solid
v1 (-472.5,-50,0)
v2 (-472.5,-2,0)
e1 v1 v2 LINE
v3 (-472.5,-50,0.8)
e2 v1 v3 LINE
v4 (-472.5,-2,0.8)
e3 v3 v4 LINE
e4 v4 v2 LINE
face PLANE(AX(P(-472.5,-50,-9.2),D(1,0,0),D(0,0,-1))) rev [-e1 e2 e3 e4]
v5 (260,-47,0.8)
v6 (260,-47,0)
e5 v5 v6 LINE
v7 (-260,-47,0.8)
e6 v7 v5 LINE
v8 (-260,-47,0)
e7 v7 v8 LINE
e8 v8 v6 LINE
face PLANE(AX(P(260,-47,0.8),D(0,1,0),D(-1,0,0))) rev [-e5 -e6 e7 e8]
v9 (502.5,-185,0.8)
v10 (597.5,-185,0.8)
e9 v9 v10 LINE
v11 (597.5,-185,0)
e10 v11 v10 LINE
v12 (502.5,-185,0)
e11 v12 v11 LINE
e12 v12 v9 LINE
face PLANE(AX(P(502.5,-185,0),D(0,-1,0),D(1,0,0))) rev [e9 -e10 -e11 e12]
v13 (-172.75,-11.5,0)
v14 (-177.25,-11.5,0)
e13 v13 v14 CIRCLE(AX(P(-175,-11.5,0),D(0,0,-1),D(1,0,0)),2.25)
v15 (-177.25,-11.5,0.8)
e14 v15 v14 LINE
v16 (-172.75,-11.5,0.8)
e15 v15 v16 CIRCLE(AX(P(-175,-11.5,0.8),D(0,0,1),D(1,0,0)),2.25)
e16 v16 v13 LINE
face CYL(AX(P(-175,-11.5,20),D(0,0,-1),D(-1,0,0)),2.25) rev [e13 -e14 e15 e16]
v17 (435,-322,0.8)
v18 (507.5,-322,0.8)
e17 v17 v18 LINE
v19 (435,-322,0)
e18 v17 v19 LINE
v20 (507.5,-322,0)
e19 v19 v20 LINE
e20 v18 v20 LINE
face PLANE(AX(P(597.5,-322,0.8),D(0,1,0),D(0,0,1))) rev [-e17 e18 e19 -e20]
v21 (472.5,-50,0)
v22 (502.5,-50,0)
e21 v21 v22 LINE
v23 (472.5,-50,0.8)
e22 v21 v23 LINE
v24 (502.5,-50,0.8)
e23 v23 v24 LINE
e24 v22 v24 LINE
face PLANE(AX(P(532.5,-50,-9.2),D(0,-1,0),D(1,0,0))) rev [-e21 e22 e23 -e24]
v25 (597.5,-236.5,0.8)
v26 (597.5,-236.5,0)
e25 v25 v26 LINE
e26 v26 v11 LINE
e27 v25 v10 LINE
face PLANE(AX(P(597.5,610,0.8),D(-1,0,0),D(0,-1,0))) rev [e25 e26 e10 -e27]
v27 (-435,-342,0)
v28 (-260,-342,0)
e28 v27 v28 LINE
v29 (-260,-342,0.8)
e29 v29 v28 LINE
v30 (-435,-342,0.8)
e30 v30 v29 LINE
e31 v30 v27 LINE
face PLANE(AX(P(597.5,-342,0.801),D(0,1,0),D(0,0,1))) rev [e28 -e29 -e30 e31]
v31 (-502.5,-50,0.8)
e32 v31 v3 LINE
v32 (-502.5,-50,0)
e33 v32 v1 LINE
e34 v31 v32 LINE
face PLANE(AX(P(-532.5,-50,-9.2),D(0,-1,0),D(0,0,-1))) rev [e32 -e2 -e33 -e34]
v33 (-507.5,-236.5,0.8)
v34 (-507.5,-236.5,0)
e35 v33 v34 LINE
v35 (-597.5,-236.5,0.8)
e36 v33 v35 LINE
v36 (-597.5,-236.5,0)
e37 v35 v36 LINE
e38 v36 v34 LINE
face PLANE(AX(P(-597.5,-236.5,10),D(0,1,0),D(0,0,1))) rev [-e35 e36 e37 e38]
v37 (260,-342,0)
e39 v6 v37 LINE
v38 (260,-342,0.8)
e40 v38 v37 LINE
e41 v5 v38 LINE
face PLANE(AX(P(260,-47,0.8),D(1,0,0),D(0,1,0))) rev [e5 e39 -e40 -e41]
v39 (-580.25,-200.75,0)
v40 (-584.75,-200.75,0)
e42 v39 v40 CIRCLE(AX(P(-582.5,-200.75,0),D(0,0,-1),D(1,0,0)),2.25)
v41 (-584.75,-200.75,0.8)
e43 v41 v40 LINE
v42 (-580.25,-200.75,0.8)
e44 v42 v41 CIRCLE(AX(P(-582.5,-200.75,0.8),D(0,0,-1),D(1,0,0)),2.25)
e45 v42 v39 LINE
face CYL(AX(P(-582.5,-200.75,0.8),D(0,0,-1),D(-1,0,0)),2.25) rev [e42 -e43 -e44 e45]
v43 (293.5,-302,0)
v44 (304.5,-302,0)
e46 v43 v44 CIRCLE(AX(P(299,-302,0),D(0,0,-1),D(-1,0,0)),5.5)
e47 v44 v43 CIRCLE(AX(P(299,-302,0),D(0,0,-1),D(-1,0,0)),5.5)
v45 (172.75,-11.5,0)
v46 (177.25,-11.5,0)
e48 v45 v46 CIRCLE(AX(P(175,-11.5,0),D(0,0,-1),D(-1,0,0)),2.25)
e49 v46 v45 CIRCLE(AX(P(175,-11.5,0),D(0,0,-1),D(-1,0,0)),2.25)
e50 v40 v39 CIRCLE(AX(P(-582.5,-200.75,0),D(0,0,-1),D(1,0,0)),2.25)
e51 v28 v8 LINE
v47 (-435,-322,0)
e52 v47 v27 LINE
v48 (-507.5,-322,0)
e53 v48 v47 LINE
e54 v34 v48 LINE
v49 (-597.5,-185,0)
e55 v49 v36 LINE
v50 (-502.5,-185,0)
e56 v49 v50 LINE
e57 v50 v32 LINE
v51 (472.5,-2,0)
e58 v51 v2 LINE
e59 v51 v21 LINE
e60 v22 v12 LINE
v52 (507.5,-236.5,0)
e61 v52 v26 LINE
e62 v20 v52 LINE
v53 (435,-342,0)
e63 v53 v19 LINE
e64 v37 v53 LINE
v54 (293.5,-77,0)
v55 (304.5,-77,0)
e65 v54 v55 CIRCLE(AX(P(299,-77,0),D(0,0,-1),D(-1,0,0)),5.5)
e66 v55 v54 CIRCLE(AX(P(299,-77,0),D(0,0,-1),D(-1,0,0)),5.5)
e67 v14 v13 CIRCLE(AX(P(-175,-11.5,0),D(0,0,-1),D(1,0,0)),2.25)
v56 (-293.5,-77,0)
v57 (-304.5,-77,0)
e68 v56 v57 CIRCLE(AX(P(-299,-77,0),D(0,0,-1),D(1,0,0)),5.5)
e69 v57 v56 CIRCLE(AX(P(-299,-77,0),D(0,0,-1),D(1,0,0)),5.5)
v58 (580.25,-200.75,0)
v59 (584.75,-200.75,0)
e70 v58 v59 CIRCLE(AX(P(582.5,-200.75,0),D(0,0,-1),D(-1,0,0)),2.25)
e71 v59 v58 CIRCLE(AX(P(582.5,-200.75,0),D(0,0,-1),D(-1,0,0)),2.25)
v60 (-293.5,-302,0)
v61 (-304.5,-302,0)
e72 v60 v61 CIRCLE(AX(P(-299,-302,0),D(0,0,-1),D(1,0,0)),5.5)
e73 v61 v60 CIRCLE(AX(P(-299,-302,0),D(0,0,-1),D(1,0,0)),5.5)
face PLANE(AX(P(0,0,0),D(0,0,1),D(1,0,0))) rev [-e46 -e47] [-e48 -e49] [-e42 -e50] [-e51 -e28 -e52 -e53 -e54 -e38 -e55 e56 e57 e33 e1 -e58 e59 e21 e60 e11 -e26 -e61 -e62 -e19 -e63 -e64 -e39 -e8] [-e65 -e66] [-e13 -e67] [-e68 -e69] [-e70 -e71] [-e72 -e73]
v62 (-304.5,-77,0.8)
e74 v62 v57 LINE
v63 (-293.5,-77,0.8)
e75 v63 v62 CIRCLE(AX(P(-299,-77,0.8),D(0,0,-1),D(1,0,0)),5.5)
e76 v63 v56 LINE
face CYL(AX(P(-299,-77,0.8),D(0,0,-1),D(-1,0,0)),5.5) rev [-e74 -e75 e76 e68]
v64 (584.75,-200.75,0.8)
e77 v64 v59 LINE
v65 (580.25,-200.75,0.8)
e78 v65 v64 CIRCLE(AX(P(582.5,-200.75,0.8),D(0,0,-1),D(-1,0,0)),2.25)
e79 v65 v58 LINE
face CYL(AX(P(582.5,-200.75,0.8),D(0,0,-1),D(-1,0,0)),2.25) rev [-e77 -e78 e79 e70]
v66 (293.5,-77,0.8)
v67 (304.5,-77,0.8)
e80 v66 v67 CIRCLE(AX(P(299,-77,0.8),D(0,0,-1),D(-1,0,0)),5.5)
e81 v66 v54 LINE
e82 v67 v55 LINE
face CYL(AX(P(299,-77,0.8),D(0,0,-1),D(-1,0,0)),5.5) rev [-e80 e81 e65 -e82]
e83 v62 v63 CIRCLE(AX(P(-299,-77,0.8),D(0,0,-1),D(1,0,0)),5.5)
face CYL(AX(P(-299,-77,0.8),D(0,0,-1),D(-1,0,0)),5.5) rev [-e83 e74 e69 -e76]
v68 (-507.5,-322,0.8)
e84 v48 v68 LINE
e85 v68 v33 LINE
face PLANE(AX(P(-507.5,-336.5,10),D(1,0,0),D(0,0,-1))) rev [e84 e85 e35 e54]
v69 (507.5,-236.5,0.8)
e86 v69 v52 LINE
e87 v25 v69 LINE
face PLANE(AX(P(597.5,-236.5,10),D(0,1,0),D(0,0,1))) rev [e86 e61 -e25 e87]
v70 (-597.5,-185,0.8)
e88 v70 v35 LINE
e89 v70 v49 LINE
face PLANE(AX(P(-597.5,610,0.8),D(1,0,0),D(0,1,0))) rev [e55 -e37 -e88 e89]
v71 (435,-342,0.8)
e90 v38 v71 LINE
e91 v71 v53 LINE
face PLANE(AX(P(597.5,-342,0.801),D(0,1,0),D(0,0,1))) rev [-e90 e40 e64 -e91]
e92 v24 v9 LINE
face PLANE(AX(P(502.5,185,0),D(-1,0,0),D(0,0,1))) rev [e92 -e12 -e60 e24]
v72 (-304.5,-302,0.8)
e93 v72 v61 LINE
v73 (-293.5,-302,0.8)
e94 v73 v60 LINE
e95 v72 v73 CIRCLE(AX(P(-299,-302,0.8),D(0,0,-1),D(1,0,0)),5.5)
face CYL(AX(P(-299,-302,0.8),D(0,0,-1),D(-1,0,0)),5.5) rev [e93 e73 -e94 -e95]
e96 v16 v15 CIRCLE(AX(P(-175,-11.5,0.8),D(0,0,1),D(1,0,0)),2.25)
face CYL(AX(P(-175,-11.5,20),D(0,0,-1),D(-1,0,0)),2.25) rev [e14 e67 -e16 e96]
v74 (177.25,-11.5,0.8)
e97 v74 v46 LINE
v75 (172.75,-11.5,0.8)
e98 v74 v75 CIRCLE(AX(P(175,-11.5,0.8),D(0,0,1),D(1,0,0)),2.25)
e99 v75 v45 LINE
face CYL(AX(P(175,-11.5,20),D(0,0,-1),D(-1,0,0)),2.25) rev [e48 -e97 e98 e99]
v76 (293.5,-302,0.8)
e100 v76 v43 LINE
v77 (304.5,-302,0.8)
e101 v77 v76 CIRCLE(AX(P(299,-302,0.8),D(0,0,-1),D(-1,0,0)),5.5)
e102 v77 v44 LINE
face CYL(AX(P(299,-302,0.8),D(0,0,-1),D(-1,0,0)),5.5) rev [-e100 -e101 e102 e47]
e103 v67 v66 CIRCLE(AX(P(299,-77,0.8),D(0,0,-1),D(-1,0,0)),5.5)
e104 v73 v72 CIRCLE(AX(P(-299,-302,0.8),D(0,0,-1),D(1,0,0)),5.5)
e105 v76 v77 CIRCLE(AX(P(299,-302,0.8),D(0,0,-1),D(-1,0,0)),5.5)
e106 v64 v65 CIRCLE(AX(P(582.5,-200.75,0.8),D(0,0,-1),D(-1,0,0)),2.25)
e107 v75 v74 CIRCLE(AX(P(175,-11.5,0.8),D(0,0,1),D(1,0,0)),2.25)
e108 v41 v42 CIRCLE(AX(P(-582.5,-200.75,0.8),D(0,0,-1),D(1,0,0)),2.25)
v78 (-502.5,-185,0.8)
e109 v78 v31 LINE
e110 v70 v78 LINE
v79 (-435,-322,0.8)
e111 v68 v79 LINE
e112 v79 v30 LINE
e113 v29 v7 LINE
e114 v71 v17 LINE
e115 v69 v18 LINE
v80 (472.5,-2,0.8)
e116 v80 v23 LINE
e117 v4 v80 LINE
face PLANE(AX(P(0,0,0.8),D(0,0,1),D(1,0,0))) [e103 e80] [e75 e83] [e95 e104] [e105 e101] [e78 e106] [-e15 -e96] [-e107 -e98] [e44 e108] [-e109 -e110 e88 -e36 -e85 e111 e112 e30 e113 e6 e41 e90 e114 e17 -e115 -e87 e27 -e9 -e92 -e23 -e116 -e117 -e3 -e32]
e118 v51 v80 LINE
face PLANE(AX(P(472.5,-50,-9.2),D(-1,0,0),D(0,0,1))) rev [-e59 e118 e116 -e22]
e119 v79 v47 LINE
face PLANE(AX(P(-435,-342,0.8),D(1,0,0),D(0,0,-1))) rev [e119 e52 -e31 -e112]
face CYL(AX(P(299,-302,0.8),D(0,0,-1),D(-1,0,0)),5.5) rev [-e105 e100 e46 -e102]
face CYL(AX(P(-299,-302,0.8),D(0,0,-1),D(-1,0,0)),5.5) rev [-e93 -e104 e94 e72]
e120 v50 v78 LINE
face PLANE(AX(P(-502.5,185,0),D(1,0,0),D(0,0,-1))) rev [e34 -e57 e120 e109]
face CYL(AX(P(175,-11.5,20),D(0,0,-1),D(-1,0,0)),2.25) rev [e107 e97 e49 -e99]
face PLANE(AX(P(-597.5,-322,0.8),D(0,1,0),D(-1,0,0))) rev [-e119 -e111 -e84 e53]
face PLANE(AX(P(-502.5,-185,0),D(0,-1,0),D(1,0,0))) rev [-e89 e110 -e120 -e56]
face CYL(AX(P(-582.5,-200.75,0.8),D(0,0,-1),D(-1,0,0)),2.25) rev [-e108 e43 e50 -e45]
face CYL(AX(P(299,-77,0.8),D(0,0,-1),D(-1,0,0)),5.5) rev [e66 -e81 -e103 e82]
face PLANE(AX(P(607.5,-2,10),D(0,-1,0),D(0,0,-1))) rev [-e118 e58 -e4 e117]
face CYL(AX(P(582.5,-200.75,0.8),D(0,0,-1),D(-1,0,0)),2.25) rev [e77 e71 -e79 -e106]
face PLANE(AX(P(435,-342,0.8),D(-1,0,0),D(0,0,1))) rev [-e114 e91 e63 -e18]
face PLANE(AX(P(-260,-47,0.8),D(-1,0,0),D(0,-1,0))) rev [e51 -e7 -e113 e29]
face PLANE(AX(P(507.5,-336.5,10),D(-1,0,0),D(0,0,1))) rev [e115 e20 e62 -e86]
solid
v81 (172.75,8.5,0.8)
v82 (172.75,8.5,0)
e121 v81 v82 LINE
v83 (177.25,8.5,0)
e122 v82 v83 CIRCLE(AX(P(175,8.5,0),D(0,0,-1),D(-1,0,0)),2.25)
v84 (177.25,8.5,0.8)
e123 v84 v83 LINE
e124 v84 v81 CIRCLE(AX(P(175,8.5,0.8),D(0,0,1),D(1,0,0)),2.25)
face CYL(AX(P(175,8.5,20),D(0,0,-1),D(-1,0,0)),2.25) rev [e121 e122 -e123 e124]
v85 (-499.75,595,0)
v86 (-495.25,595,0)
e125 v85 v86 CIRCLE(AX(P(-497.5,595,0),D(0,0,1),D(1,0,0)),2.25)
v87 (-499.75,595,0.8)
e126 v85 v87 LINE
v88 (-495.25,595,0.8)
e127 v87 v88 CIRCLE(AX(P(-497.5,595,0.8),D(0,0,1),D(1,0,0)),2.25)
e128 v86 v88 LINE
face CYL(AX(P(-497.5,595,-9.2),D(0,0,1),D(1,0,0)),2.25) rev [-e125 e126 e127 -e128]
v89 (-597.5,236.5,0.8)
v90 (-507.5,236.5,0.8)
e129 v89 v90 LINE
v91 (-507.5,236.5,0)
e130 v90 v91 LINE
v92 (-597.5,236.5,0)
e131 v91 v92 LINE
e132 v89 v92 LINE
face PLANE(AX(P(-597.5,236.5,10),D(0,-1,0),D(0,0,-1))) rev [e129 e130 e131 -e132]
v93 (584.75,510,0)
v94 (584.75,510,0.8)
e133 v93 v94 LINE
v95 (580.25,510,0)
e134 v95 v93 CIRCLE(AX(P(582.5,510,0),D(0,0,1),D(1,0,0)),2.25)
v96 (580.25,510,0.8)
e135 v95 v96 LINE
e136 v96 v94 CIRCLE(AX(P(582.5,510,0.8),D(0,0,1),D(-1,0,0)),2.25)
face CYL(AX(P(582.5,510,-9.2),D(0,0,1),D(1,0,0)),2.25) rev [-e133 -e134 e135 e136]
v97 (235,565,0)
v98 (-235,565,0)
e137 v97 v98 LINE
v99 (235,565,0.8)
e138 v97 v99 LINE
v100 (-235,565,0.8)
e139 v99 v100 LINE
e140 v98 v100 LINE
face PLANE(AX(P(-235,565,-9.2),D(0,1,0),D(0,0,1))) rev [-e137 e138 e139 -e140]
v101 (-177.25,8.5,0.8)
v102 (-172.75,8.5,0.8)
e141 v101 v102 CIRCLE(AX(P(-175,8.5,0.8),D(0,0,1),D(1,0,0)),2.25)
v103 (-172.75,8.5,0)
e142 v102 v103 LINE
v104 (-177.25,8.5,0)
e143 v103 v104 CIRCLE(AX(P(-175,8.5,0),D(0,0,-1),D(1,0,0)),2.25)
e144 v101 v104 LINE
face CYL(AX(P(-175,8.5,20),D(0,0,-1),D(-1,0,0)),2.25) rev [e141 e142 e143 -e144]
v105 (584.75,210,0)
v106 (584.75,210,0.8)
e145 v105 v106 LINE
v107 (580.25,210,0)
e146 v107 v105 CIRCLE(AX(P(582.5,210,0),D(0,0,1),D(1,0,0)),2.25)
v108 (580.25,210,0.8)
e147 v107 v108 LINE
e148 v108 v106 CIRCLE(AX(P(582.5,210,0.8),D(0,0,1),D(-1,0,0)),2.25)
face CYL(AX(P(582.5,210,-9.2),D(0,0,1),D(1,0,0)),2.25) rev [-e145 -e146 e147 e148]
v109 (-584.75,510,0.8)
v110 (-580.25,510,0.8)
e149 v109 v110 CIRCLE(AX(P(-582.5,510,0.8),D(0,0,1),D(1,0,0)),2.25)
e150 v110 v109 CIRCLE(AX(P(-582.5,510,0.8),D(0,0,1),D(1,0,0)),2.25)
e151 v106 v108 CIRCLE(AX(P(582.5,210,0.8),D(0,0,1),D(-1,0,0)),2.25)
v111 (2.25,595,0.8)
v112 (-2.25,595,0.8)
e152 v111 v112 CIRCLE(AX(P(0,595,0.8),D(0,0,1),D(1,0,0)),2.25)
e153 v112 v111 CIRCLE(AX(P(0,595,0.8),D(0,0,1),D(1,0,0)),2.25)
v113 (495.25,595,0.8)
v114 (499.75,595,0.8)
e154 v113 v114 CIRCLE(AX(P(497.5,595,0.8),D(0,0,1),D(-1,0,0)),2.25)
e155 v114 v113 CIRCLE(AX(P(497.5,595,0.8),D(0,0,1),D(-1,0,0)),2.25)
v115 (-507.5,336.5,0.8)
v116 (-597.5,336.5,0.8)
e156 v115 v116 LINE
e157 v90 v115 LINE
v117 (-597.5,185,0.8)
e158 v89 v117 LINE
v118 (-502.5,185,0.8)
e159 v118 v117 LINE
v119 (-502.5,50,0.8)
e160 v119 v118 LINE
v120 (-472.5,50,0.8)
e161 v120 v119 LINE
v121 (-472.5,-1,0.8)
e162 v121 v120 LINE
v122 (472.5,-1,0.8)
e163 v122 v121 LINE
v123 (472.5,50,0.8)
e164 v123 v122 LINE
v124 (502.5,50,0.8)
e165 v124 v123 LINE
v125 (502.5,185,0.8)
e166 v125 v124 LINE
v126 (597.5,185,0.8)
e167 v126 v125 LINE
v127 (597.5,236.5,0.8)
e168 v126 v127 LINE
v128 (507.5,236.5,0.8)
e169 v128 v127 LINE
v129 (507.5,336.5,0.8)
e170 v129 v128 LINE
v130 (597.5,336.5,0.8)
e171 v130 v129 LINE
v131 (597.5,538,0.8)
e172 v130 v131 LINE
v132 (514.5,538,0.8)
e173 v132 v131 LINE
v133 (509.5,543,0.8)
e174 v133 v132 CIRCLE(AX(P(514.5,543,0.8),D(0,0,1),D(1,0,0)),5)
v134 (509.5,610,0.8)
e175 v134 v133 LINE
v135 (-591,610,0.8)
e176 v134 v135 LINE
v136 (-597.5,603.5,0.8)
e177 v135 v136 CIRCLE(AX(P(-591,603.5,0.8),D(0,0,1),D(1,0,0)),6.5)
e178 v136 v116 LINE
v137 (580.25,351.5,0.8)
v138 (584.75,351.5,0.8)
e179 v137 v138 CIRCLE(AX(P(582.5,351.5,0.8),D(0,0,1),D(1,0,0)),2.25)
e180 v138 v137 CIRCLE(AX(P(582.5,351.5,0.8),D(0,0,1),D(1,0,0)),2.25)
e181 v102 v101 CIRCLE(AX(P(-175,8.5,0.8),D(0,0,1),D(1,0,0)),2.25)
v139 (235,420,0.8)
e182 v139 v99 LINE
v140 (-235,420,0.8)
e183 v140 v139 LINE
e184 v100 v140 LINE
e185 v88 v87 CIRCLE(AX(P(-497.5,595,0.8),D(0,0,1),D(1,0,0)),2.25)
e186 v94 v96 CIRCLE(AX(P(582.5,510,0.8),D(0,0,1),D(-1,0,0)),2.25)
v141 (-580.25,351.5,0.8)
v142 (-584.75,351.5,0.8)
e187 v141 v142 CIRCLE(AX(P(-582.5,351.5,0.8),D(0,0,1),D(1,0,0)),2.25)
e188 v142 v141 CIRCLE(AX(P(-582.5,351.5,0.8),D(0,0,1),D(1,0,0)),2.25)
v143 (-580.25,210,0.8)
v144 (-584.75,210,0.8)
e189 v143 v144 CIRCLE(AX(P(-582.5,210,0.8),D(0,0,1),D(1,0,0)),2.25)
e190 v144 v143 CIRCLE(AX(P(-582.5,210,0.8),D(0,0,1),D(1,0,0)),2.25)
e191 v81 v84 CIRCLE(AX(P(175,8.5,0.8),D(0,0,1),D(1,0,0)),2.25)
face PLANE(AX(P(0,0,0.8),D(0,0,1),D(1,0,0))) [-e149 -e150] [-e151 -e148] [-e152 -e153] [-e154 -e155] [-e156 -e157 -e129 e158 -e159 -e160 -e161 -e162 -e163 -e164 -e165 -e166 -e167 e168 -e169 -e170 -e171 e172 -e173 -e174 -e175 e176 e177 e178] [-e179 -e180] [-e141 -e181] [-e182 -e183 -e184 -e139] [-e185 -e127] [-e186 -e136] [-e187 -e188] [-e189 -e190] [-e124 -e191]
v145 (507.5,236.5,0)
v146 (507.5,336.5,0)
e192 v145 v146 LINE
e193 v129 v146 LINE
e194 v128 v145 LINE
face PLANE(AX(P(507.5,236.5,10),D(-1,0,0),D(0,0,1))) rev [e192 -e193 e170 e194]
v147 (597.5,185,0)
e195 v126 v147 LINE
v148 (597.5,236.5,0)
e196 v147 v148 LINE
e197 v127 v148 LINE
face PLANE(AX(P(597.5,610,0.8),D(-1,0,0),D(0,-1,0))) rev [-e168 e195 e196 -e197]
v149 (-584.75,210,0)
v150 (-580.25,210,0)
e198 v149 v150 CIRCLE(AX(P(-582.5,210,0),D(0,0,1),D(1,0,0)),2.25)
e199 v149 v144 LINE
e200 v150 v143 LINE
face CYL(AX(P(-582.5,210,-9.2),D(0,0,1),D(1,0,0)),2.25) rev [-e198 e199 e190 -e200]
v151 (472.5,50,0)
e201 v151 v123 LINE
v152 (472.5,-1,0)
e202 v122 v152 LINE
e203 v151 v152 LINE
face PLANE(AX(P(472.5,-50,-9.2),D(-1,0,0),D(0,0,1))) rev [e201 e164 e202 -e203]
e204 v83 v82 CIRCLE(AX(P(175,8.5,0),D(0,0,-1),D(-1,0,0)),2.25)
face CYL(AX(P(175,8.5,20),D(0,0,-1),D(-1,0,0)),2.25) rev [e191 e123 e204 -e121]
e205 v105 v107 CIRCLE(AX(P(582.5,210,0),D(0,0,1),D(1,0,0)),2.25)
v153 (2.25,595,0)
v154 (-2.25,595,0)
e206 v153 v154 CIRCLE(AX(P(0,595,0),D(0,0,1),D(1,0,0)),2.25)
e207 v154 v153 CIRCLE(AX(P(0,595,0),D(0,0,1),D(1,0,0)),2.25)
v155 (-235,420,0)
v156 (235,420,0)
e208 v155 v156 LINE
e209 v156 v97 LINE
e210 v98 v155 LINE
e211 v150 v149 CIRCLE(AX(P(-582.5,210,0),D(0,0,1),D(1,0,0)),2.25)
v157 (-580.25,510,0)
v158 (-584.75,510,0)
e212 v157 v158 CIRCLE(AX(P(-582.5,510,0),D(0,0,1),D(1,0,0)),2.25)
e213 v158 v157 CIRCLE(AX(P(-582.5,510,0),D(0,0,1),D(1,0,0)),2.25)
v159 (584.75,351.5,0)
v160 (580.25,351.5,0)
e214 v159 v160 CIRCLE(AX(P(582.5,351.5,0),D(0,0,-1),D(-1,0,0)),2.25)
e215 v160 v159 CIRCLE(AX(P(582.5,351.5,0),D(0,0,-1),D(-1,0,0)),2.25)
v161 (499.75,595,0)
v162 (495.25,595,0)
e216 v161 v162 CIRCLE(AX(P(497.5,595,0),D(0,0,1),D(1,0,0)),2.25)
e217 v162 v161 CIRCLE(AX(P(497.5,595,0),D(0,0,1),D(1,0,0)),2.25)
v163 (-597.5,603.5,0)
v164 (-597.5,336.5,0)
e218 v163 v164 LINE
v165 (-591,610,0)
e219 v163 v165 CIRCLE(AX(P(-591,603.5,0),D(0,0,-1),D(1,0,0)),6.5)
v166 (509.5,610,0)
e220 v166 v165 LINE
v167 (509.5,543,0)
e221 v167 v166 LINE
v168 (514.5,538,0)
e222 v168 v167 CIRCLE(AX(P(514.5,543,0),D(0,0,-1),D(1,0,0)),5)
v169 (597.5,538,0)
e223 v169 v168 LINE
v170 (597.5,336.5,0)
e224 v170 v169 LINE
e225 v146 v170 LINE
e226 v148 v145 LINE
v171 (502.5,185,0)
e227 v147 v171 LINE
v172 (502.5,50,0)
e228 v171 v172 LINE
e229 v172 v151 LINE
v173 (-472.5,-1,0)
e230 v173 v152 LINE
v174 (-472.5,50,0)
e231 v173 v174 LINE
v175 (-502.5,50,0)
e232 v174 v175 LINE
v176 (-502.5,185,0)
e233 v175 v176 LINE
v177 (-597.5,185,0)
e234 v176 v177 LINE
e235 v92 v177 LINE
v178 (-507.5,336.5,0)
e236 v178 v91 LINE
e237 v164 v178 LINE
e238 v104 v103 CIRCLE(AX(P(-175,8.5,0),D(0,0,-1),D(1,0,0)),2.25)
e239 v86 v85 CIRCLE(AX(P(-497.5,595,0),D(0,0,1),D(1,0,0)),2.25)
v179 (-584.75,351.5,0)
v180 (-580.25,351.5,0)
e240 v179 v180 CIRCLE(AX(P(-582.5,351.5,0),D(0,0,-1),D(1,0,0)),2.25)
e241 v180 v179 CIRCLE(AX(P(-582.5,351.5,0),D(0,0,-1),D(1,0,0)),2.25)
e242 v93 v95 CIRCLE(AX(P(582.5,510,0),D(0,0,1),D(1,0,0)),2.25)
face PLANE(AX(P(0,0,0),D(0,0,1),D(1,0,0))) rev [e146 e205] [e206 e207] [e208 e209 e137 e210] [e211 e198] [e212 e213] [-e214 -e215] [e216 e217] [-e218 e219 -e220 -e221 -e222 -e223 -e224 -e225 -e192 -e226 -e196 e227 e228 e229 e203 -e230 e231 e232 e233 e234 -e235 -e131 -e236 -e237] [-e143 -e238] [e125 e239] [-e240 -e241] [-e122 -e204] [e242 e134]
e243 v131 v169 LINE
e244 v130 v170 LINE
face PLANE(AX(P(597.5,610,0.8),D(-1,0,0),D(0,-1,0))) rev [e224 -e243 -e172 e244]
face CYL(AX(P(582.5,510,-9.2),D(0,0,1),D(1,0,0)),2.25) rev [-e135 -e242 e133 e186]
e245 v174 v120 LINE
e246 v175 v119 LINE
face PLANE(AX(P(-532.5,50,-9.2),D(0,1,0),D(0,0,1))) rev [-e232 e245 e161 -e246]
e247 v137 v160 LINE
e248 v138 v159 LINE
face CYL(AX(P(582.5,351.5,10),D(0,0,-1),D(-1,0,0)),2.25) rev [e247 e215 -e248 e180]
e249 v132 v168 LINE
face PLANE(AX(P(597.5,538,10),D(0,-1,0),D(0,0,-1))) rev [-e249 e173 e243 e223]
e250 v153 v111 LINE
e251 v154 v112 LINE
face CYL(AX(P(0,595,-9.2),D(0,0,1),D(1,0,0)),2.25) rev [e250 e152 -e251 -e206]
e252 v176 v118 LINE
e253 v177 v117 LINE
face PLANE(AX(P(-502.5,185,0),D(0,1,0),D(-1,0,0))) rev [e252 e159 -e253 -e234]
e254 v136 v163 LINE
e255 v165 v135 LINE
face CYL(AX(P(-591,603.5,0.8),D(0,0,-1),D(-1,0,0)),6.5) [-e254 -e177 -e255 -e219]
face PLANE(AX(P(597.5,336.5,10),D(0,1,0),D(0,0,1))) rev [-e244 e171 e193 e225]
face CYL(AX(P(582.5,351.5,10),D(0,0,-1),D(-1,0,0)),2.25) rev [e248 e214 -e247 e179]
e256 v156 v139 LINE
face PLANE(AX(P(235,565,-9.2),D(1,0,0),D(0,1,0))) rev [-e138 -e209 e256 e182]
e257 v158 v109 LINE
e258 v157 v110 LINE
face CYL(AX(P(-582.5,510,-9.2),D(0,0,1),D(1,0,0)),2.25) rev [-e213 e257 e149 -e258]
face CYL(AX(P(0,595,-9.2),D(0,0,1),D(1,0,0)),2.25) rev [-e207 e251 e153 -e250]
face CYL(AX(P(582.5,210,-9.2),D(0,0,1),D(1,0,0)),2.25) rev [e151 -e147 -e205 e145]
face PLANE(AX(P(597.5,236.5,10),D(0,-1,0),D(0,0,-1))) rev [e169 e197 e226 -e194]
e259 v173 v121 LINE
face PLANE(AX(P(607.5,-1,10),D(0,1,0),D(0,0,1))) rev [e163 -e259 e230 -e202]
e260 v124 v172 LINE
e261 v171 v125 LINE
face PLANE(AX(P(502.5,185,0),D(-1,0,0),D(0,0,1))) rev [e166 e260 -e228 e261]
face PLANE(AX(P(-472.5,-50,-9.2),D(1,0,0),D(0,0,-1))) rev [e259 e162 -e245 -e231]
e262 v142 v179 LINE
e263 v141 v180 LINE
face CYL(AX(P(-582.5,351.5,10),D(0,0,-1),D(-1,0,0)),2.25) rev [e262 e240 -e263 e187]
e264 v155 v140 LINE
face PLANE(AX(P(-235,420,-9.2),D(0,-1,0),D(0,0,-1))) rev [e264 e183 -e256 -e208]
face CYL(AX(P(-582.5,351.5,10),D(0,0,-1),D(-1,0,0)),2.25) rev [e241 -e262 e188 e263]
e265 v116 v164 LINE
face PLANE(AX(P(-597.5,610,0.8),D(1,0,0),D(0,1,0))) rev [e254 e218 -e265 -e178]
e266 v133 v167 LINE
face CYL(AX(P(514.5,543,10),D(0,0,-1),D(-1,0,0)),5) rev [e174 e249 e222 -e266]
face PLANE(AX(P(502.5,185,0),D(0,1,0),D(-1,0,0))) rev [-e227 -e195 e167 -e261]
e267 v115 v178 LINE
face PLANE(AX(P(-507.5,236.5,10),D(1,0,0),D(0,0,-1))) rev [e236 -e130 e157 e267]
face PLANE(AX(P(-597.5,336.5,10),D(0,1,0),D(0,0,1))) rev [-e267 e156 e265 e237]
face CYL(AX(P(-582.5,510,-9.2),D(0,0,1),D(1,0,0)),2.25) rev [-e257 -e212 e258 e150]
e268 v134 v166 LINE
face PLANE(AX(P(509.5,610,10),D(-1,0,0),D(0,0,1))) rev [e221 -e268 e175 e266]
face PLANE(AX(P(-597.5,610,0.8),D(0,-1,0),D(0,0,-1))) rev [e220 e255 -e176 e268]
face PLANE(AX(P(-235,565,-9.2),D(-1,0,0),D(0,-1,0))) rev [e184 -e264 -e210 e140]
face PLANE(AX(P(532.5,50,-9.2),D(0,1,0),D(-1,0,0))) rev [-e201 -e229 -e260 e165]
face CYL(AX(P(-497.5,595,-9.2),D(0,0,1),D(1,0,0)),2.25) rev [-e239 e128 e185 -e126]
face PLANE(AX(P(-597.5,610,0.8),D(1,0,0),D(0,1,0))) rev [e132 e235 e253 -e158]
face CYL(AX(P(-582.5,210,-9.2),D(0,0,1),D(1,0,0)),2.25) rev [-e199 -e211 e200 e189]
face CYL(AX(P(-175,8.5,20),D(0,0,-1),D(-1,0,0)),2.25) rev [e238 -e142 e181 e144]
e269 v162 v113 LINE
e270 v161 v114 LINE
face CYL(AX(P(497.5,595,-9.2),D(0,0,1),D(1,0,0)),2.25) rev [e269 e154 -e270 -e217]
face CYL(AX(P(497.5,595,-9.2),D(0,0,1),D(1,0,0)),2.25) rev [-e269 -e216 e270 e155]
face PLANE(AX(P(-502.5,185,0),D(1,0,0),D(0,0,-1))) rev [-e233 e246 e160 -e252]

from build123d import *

# Parameters (mm, degrees)
SKETCH_1_W             = 1195
SKETCH_1_H             = 1360
EXTRUDE_1_DEPTH        = 0.8
SKETCH_2_W             = 190
SKETCH_2_H             = 370
CUT_EXTRUDE_2618_DEPTH = 959.909218852
FILLET_6_R             = 6.5
FILLET_7_R             = 6.5
SKETCH_3_W             = 470
SKETCH_3_H             = 145
CUT_EXTRUDE_3491_DEPTH = 10
SKETCH_8_R             = 5.5
SKETCH_8_W             = 520
SKETCH_8_H             = 295
CUT_EXTRUDE_4077_DEPTH = 959.909218852
SKETCH_4_W             = 60
SKETCH_4_H             = 100
CUT_EXTRUDE_4742_DEPTH = 10
SKETCH_5_R             = 2.25
CUT_EXTRUDE_5780_DEPTH = 10
SKETCH_7_W             = 90
SKETCH_7_H             = 100
CUT_EXTRUDE_6423_DEPTH = 10
SKETCH_17_R            = 2.25
CUT_EXTRUDE_4_DEPTH    = 959.909218852
CUT_EXTRUDE_7850_REACH = 960.909
SKETCH_18_W            = 1195
SKETCH_18_H            = 408
SKETCH_19_W            = 162.5
SKETCH_19_H            = 20
CUT_EXTRUDE_8511_DEPTH = 854.877561481
CUT_EXTRUDE_1_DEPTH    = 10
SKETCH_21_R            = 2.25
CUT_EXTRUDE_2_DEPTH    = 10
SKETCH_22_W            = 1215
SKETCH_22_H            = 1
CUT_EXTRUDE_4_2_DEPTH  = 10
SKETCH_23_R            = 2.25
CUT_EXTRUDE_5_DEPTH    = 20


with BuildPart() as part:
    # 草图1 → 凸台-拉伸1 (new body)
    with BuildSketch(Plane.XY):
        with Locations((0, -70)):
            Rectangle(SKETCH_1_W, SKETCH_1_H)
    extrude(amount=EXTRUDE_1_DEPTH)

    # 草图2 → Cut-Extrude 2618 (cut, through all)
    with BuildSketch(Plane.XY.offset(0.8)):
        with Locations((-597.5, 0)):
            Rectangle(SKETCH_2_W, SKETCH_2_H)
        with Locations((597.5, 0)):
            Rectangle(SKETCH_2_W, SKETCH_2_H)
    extrude(amount=-CUT_EXTRUDE_2618_DEPTH, mode=Mode.SUBTRACT)

    # 圆角6
    fillet_6_edges = [part.edges().sort_by_distance(p)[0] for p in [
        (-597.5, 610, 0.4),
    ]]
    fillet(fillet_6_edges, radius=FILLET_6_R)

    # 圆角7
    fillet_7_edges = [part.edges().sort_by_distance(p)[0] for p in [
        (597.5, 610, 0.4),
    ]]
    fillet(fillet_7_edges, radius=FILLET_7_R)

    # 草图3 → Cut-Extrude 3491 (cut)
    with BuildSketch(Plane.XY.offset(0.8)):
        with Locations((0, 492.5)):
            Rectangle(SKETCH_3_W, SKETCH_3_H)
    extrude(amount=-CUT_EXTRUDE_3491_DEPTH, mode=Mode.SUBTRACT)

    # 草图8 → Cut-Extrude 4077 (cut, through all)
    with BuildSketch(Plane(origin=(0, 0, 0), x_dir=(-1, 0, 0), z_dir=(0, 0, -1))):
        with Locations((-299, -77)):
            Circle(SKETCH_8_R)
        with Locations((-299, -302)):
            Circle(SKETCH_8_R)
        with Locations(Location((299, -302, 0), (0, 0, 180))):
            Circle(SKETCH_8_R)
        with Locations(Location((299, -77, 0), (0, 0, 180))):
            Circle(SKETCH_8_R)
        with Locations((0, -194.5)):
            Rectangle(SKETCH_8_W, SKETCH_8_H)
    extrude(amount=-CUT_EXTRUDE_4077_DEPTH, mode=Mode.SUBTRACT)

    # 草图4 → Cut-Extrude 4742 (cut)
    with BuildSketch(Plane.XY.offset(0.8)):
        with Locations((-502.5, 0)):
            Rectangle(SKETCH_4_W, SKETCH_4_H)
        with Locations((502.5, 0)):
            Rectangle(SKETCH_4_W, SKETCH_4_H)
    extrude(amount=-CUT_EXTRUDE_4742_DEPTH, mode=Mode.SUBTRACT)

    # 草图5 → Cut-Extrude 5780 (cut)
    with BuildSketch(Plane.XY.offset(0.8)):
        with Locations((-497.5, 595)):
            Circle(SKETCH_5_R)
        with Locations((-582.5, 510)):
            Circle(SKETCH_5_R)
        with Locations((582.5, 510)):
            Circle(SKETCH_5_R)
        with Locations((497.5, 595)):
            Circle(SKETCH_5_R)
        with Locations((0, 595)):
            Circle(SKETCH_5_R)
        with Locations((-582.5, 210)):
            Circle(SKETCH_5_R)
        with Locations((582.5, 210)):
            Circle(SKETCH_5_R)
    extrude(amount=-CUT_EXTRUDE_5780_DEPTH, mode=Mode.SUBTRACT)

    # 草图7 → Cut-Extrude 6423 (cut)
    with BuildSketch(Plane(origin=(0, 0, 0), x_dir=(-1, 0, 0), z_dir=(0, 0, -1))):
        with Locations((552.5, -286.5)):
            Rectangle(SKETCH_7_W, SKETCH_7_H)
        with Locations((-552.5, 286.5)):
            Rectangle(SKETCH_7_W, SKETCH_7_H)
        with Locations((552.5, 286.5)):
            Rectangle(SKETCH_7_W, SKETCH_7_H)
        with Locations((-552.5, -286.5)):
            Rectangle(SKETCH_7_W, SKETCH_7_H)
    extrude(amount=-CUT_EXTRUDE_6423_DEPTH, mode=Mode.SUBTRACT)

    # 草图17 → Cut-Extrude 4 (cut, through all)
    with BuildSketch(Plane(origin=(0, 0, 0), x_dir=(-1, 0, 0), z_dir=(0, 0, -1))):
        with Locations((-582.5, -200.75)):
            Circle(SKETCH_17_R)
        with Locations(Location((582.5, -200.75, 0), (0, 0, 180))):
            Circle(SKETCH_17_R)
    extrude(amount=-CUT_EXTRUDE_4_DEPTH, mode=Mode.SUBTRACT)

    # 草图18 → Cut-Extrude 7850 (cut, up to next)
    with BuildSketch(Plane(origin=(0, 0, 0), x_dir=(-1, 0, 0), z_dir=(0, 0, -1)), mode=Mode.PRIVATE) as cut_extrude_7850_sk1:
        with Locations((0, -546)):
            Rectangle(SKETCH_18_W, SKETCH_18_H)
    cut_extrude_7850_tool1 = extrude(cut_extrude_7850_sk1.sketch, amount=-CUT_EXTRUDE_7850_REACH, mode=Mode.PRIVATE) & part.part
    add(cut_extrude_7850_tool1.solids().sort_by_distance((0, -546, 0))[0], mode=Mode.SUBTRACT)

    # 草图19 → Cut-Extrude 8511 (cut, through all)
    with BuildSketch(Plane(origin=(0, 0, 0), x_dir=(-1, 0, 0), z_dir=(0, 0, -1))):
        with Locations((-516.25, -332)):
            Rectangle(SKETCH_19_W, SKETCH_19_H)
        with Locations((516.25, -332)):
            Rectangle(SKETCH_19_W, SKETCH_19_H)
    extrude(amount=-CUT_EXTRUDE_8511_DEPTH, mode=Mode.SUBTRACT)

    # 草图20 → Cut-Extrude 1 (cut)
    with BuildSketch(Plane(origin=(0, 0, 0), x_dir=(-1, 0, 0), z_dir=(0, 0, -1))):
        with BuildLine():
            Line((-597.5, 610), (-509.5, 610))
            Line((-509.5, 610), (-509.5, 543))
            ThreePointArc((-509.5, 543), (-510.964466094, 539.464466094), (-514.5, 538))
            Line((-514.5, 538), (-597.5, 538))
            Line((-597.5, 538), (-597.5, 610))
        make_face()
    extrude(amount=-CUT_EXTRUDE_1_DEPTH, mode=Mode.SUBTRACT)

    # 草图21 → Cut-Extrude 2 (cut)
    with BuildSketch(Plane(origin=(0, 0, 0), x_dir=(-1, 0, 0), z_dir=(0, 0, -1))):
        with Locations((-582.5, 351.5)):
            Circle(SKETCH_21_R)
        with Locations(Location((582.5, 351.5, 0), (0, 0, 180))):
            Circle(SKETCH_21_R)
    extrude(amount=-CUT_EXTRUDE_2_DEPTH, mode=Mode.SUBTRACT)

    # 草图22 → Cut-Extrude 4 2 (cut)
    with BuildSketch(Plane(origin=(0, 0, 0), x_dir=(-1, 0, 0), z_dir=(0, 0, -1))):
        with Locations((0, -1.5)):
            Rectangle(SKETCH_22_W, SKETCH_22_H)
    extrude(amount=-CUT_EXTRUDE_4_2_DEPTH, mode=Mode.SUBTRACT)


with BuildPart() as cut_extrude_4_2_piece_1:
    # of the separate pieces the step leaves, piece 1, a body of its own (cut_extrude_4_2_pieces)
    add(part.part.solids().sort_by_distance((-591, 610, 0))[0])


with BuildPart() as cut_extrude_4_2_piece_2:
    # of the separate pieces the step leaves, piece 2, a body of its own (cut_extrude_4_2_pieces)
    add(part.part.solids().sort_by_distance((-472.5, -2, 0))[0])


with BuildPart() as cut_extrude_5_tool:
    # 草图23 → 切除-拉伸5 (new body)
    with BuildSketch(Plane(origin=(0, 0, 0), x_dir=(-1, 0, 0), z_dir=(0, 0, -1))):
        with Locations((-175, -11.5)):
            Circle(SKETCH_23_R)
        with Locations(Location((175, -11.5, 0), (0, 0, 180))):
            Circle(SKETCH_23_R)
        with Locations((-175, 8.5)):
            Circle(SKETCH_23_R)
        with Locations(Location((175, 8.5, 0), (0, 0, 180))):
            Circle(SKETCH_23_R)
    extrude(amount=-CUT_EXTRUDE_5_DEPTH)


with BuildPart() as cut_extrude_4_2_piece_1_1:
    add(cut_extrude_4_2_piece_1.part)

    # 切除-拉伸5: cut by cut_extrude_5_tool
    add(cut_extrude_5_tool.part, mode=Mode.SUBTRACT)


with BuildPart() as cut_extrude_4_2_piece_2_1:
    add(cut_extrude_4_2_piece_2.part)

    # 切除-拉伸5: cut by cut_extrude_5_tool
    add(cut_extrude_5_tool.part, mode=Mode.SUBTRACT)


solid = Compound([cut_extrude_4_2_piece_1_1.part, cut_extrude_4_2_piece_2_1.part])
